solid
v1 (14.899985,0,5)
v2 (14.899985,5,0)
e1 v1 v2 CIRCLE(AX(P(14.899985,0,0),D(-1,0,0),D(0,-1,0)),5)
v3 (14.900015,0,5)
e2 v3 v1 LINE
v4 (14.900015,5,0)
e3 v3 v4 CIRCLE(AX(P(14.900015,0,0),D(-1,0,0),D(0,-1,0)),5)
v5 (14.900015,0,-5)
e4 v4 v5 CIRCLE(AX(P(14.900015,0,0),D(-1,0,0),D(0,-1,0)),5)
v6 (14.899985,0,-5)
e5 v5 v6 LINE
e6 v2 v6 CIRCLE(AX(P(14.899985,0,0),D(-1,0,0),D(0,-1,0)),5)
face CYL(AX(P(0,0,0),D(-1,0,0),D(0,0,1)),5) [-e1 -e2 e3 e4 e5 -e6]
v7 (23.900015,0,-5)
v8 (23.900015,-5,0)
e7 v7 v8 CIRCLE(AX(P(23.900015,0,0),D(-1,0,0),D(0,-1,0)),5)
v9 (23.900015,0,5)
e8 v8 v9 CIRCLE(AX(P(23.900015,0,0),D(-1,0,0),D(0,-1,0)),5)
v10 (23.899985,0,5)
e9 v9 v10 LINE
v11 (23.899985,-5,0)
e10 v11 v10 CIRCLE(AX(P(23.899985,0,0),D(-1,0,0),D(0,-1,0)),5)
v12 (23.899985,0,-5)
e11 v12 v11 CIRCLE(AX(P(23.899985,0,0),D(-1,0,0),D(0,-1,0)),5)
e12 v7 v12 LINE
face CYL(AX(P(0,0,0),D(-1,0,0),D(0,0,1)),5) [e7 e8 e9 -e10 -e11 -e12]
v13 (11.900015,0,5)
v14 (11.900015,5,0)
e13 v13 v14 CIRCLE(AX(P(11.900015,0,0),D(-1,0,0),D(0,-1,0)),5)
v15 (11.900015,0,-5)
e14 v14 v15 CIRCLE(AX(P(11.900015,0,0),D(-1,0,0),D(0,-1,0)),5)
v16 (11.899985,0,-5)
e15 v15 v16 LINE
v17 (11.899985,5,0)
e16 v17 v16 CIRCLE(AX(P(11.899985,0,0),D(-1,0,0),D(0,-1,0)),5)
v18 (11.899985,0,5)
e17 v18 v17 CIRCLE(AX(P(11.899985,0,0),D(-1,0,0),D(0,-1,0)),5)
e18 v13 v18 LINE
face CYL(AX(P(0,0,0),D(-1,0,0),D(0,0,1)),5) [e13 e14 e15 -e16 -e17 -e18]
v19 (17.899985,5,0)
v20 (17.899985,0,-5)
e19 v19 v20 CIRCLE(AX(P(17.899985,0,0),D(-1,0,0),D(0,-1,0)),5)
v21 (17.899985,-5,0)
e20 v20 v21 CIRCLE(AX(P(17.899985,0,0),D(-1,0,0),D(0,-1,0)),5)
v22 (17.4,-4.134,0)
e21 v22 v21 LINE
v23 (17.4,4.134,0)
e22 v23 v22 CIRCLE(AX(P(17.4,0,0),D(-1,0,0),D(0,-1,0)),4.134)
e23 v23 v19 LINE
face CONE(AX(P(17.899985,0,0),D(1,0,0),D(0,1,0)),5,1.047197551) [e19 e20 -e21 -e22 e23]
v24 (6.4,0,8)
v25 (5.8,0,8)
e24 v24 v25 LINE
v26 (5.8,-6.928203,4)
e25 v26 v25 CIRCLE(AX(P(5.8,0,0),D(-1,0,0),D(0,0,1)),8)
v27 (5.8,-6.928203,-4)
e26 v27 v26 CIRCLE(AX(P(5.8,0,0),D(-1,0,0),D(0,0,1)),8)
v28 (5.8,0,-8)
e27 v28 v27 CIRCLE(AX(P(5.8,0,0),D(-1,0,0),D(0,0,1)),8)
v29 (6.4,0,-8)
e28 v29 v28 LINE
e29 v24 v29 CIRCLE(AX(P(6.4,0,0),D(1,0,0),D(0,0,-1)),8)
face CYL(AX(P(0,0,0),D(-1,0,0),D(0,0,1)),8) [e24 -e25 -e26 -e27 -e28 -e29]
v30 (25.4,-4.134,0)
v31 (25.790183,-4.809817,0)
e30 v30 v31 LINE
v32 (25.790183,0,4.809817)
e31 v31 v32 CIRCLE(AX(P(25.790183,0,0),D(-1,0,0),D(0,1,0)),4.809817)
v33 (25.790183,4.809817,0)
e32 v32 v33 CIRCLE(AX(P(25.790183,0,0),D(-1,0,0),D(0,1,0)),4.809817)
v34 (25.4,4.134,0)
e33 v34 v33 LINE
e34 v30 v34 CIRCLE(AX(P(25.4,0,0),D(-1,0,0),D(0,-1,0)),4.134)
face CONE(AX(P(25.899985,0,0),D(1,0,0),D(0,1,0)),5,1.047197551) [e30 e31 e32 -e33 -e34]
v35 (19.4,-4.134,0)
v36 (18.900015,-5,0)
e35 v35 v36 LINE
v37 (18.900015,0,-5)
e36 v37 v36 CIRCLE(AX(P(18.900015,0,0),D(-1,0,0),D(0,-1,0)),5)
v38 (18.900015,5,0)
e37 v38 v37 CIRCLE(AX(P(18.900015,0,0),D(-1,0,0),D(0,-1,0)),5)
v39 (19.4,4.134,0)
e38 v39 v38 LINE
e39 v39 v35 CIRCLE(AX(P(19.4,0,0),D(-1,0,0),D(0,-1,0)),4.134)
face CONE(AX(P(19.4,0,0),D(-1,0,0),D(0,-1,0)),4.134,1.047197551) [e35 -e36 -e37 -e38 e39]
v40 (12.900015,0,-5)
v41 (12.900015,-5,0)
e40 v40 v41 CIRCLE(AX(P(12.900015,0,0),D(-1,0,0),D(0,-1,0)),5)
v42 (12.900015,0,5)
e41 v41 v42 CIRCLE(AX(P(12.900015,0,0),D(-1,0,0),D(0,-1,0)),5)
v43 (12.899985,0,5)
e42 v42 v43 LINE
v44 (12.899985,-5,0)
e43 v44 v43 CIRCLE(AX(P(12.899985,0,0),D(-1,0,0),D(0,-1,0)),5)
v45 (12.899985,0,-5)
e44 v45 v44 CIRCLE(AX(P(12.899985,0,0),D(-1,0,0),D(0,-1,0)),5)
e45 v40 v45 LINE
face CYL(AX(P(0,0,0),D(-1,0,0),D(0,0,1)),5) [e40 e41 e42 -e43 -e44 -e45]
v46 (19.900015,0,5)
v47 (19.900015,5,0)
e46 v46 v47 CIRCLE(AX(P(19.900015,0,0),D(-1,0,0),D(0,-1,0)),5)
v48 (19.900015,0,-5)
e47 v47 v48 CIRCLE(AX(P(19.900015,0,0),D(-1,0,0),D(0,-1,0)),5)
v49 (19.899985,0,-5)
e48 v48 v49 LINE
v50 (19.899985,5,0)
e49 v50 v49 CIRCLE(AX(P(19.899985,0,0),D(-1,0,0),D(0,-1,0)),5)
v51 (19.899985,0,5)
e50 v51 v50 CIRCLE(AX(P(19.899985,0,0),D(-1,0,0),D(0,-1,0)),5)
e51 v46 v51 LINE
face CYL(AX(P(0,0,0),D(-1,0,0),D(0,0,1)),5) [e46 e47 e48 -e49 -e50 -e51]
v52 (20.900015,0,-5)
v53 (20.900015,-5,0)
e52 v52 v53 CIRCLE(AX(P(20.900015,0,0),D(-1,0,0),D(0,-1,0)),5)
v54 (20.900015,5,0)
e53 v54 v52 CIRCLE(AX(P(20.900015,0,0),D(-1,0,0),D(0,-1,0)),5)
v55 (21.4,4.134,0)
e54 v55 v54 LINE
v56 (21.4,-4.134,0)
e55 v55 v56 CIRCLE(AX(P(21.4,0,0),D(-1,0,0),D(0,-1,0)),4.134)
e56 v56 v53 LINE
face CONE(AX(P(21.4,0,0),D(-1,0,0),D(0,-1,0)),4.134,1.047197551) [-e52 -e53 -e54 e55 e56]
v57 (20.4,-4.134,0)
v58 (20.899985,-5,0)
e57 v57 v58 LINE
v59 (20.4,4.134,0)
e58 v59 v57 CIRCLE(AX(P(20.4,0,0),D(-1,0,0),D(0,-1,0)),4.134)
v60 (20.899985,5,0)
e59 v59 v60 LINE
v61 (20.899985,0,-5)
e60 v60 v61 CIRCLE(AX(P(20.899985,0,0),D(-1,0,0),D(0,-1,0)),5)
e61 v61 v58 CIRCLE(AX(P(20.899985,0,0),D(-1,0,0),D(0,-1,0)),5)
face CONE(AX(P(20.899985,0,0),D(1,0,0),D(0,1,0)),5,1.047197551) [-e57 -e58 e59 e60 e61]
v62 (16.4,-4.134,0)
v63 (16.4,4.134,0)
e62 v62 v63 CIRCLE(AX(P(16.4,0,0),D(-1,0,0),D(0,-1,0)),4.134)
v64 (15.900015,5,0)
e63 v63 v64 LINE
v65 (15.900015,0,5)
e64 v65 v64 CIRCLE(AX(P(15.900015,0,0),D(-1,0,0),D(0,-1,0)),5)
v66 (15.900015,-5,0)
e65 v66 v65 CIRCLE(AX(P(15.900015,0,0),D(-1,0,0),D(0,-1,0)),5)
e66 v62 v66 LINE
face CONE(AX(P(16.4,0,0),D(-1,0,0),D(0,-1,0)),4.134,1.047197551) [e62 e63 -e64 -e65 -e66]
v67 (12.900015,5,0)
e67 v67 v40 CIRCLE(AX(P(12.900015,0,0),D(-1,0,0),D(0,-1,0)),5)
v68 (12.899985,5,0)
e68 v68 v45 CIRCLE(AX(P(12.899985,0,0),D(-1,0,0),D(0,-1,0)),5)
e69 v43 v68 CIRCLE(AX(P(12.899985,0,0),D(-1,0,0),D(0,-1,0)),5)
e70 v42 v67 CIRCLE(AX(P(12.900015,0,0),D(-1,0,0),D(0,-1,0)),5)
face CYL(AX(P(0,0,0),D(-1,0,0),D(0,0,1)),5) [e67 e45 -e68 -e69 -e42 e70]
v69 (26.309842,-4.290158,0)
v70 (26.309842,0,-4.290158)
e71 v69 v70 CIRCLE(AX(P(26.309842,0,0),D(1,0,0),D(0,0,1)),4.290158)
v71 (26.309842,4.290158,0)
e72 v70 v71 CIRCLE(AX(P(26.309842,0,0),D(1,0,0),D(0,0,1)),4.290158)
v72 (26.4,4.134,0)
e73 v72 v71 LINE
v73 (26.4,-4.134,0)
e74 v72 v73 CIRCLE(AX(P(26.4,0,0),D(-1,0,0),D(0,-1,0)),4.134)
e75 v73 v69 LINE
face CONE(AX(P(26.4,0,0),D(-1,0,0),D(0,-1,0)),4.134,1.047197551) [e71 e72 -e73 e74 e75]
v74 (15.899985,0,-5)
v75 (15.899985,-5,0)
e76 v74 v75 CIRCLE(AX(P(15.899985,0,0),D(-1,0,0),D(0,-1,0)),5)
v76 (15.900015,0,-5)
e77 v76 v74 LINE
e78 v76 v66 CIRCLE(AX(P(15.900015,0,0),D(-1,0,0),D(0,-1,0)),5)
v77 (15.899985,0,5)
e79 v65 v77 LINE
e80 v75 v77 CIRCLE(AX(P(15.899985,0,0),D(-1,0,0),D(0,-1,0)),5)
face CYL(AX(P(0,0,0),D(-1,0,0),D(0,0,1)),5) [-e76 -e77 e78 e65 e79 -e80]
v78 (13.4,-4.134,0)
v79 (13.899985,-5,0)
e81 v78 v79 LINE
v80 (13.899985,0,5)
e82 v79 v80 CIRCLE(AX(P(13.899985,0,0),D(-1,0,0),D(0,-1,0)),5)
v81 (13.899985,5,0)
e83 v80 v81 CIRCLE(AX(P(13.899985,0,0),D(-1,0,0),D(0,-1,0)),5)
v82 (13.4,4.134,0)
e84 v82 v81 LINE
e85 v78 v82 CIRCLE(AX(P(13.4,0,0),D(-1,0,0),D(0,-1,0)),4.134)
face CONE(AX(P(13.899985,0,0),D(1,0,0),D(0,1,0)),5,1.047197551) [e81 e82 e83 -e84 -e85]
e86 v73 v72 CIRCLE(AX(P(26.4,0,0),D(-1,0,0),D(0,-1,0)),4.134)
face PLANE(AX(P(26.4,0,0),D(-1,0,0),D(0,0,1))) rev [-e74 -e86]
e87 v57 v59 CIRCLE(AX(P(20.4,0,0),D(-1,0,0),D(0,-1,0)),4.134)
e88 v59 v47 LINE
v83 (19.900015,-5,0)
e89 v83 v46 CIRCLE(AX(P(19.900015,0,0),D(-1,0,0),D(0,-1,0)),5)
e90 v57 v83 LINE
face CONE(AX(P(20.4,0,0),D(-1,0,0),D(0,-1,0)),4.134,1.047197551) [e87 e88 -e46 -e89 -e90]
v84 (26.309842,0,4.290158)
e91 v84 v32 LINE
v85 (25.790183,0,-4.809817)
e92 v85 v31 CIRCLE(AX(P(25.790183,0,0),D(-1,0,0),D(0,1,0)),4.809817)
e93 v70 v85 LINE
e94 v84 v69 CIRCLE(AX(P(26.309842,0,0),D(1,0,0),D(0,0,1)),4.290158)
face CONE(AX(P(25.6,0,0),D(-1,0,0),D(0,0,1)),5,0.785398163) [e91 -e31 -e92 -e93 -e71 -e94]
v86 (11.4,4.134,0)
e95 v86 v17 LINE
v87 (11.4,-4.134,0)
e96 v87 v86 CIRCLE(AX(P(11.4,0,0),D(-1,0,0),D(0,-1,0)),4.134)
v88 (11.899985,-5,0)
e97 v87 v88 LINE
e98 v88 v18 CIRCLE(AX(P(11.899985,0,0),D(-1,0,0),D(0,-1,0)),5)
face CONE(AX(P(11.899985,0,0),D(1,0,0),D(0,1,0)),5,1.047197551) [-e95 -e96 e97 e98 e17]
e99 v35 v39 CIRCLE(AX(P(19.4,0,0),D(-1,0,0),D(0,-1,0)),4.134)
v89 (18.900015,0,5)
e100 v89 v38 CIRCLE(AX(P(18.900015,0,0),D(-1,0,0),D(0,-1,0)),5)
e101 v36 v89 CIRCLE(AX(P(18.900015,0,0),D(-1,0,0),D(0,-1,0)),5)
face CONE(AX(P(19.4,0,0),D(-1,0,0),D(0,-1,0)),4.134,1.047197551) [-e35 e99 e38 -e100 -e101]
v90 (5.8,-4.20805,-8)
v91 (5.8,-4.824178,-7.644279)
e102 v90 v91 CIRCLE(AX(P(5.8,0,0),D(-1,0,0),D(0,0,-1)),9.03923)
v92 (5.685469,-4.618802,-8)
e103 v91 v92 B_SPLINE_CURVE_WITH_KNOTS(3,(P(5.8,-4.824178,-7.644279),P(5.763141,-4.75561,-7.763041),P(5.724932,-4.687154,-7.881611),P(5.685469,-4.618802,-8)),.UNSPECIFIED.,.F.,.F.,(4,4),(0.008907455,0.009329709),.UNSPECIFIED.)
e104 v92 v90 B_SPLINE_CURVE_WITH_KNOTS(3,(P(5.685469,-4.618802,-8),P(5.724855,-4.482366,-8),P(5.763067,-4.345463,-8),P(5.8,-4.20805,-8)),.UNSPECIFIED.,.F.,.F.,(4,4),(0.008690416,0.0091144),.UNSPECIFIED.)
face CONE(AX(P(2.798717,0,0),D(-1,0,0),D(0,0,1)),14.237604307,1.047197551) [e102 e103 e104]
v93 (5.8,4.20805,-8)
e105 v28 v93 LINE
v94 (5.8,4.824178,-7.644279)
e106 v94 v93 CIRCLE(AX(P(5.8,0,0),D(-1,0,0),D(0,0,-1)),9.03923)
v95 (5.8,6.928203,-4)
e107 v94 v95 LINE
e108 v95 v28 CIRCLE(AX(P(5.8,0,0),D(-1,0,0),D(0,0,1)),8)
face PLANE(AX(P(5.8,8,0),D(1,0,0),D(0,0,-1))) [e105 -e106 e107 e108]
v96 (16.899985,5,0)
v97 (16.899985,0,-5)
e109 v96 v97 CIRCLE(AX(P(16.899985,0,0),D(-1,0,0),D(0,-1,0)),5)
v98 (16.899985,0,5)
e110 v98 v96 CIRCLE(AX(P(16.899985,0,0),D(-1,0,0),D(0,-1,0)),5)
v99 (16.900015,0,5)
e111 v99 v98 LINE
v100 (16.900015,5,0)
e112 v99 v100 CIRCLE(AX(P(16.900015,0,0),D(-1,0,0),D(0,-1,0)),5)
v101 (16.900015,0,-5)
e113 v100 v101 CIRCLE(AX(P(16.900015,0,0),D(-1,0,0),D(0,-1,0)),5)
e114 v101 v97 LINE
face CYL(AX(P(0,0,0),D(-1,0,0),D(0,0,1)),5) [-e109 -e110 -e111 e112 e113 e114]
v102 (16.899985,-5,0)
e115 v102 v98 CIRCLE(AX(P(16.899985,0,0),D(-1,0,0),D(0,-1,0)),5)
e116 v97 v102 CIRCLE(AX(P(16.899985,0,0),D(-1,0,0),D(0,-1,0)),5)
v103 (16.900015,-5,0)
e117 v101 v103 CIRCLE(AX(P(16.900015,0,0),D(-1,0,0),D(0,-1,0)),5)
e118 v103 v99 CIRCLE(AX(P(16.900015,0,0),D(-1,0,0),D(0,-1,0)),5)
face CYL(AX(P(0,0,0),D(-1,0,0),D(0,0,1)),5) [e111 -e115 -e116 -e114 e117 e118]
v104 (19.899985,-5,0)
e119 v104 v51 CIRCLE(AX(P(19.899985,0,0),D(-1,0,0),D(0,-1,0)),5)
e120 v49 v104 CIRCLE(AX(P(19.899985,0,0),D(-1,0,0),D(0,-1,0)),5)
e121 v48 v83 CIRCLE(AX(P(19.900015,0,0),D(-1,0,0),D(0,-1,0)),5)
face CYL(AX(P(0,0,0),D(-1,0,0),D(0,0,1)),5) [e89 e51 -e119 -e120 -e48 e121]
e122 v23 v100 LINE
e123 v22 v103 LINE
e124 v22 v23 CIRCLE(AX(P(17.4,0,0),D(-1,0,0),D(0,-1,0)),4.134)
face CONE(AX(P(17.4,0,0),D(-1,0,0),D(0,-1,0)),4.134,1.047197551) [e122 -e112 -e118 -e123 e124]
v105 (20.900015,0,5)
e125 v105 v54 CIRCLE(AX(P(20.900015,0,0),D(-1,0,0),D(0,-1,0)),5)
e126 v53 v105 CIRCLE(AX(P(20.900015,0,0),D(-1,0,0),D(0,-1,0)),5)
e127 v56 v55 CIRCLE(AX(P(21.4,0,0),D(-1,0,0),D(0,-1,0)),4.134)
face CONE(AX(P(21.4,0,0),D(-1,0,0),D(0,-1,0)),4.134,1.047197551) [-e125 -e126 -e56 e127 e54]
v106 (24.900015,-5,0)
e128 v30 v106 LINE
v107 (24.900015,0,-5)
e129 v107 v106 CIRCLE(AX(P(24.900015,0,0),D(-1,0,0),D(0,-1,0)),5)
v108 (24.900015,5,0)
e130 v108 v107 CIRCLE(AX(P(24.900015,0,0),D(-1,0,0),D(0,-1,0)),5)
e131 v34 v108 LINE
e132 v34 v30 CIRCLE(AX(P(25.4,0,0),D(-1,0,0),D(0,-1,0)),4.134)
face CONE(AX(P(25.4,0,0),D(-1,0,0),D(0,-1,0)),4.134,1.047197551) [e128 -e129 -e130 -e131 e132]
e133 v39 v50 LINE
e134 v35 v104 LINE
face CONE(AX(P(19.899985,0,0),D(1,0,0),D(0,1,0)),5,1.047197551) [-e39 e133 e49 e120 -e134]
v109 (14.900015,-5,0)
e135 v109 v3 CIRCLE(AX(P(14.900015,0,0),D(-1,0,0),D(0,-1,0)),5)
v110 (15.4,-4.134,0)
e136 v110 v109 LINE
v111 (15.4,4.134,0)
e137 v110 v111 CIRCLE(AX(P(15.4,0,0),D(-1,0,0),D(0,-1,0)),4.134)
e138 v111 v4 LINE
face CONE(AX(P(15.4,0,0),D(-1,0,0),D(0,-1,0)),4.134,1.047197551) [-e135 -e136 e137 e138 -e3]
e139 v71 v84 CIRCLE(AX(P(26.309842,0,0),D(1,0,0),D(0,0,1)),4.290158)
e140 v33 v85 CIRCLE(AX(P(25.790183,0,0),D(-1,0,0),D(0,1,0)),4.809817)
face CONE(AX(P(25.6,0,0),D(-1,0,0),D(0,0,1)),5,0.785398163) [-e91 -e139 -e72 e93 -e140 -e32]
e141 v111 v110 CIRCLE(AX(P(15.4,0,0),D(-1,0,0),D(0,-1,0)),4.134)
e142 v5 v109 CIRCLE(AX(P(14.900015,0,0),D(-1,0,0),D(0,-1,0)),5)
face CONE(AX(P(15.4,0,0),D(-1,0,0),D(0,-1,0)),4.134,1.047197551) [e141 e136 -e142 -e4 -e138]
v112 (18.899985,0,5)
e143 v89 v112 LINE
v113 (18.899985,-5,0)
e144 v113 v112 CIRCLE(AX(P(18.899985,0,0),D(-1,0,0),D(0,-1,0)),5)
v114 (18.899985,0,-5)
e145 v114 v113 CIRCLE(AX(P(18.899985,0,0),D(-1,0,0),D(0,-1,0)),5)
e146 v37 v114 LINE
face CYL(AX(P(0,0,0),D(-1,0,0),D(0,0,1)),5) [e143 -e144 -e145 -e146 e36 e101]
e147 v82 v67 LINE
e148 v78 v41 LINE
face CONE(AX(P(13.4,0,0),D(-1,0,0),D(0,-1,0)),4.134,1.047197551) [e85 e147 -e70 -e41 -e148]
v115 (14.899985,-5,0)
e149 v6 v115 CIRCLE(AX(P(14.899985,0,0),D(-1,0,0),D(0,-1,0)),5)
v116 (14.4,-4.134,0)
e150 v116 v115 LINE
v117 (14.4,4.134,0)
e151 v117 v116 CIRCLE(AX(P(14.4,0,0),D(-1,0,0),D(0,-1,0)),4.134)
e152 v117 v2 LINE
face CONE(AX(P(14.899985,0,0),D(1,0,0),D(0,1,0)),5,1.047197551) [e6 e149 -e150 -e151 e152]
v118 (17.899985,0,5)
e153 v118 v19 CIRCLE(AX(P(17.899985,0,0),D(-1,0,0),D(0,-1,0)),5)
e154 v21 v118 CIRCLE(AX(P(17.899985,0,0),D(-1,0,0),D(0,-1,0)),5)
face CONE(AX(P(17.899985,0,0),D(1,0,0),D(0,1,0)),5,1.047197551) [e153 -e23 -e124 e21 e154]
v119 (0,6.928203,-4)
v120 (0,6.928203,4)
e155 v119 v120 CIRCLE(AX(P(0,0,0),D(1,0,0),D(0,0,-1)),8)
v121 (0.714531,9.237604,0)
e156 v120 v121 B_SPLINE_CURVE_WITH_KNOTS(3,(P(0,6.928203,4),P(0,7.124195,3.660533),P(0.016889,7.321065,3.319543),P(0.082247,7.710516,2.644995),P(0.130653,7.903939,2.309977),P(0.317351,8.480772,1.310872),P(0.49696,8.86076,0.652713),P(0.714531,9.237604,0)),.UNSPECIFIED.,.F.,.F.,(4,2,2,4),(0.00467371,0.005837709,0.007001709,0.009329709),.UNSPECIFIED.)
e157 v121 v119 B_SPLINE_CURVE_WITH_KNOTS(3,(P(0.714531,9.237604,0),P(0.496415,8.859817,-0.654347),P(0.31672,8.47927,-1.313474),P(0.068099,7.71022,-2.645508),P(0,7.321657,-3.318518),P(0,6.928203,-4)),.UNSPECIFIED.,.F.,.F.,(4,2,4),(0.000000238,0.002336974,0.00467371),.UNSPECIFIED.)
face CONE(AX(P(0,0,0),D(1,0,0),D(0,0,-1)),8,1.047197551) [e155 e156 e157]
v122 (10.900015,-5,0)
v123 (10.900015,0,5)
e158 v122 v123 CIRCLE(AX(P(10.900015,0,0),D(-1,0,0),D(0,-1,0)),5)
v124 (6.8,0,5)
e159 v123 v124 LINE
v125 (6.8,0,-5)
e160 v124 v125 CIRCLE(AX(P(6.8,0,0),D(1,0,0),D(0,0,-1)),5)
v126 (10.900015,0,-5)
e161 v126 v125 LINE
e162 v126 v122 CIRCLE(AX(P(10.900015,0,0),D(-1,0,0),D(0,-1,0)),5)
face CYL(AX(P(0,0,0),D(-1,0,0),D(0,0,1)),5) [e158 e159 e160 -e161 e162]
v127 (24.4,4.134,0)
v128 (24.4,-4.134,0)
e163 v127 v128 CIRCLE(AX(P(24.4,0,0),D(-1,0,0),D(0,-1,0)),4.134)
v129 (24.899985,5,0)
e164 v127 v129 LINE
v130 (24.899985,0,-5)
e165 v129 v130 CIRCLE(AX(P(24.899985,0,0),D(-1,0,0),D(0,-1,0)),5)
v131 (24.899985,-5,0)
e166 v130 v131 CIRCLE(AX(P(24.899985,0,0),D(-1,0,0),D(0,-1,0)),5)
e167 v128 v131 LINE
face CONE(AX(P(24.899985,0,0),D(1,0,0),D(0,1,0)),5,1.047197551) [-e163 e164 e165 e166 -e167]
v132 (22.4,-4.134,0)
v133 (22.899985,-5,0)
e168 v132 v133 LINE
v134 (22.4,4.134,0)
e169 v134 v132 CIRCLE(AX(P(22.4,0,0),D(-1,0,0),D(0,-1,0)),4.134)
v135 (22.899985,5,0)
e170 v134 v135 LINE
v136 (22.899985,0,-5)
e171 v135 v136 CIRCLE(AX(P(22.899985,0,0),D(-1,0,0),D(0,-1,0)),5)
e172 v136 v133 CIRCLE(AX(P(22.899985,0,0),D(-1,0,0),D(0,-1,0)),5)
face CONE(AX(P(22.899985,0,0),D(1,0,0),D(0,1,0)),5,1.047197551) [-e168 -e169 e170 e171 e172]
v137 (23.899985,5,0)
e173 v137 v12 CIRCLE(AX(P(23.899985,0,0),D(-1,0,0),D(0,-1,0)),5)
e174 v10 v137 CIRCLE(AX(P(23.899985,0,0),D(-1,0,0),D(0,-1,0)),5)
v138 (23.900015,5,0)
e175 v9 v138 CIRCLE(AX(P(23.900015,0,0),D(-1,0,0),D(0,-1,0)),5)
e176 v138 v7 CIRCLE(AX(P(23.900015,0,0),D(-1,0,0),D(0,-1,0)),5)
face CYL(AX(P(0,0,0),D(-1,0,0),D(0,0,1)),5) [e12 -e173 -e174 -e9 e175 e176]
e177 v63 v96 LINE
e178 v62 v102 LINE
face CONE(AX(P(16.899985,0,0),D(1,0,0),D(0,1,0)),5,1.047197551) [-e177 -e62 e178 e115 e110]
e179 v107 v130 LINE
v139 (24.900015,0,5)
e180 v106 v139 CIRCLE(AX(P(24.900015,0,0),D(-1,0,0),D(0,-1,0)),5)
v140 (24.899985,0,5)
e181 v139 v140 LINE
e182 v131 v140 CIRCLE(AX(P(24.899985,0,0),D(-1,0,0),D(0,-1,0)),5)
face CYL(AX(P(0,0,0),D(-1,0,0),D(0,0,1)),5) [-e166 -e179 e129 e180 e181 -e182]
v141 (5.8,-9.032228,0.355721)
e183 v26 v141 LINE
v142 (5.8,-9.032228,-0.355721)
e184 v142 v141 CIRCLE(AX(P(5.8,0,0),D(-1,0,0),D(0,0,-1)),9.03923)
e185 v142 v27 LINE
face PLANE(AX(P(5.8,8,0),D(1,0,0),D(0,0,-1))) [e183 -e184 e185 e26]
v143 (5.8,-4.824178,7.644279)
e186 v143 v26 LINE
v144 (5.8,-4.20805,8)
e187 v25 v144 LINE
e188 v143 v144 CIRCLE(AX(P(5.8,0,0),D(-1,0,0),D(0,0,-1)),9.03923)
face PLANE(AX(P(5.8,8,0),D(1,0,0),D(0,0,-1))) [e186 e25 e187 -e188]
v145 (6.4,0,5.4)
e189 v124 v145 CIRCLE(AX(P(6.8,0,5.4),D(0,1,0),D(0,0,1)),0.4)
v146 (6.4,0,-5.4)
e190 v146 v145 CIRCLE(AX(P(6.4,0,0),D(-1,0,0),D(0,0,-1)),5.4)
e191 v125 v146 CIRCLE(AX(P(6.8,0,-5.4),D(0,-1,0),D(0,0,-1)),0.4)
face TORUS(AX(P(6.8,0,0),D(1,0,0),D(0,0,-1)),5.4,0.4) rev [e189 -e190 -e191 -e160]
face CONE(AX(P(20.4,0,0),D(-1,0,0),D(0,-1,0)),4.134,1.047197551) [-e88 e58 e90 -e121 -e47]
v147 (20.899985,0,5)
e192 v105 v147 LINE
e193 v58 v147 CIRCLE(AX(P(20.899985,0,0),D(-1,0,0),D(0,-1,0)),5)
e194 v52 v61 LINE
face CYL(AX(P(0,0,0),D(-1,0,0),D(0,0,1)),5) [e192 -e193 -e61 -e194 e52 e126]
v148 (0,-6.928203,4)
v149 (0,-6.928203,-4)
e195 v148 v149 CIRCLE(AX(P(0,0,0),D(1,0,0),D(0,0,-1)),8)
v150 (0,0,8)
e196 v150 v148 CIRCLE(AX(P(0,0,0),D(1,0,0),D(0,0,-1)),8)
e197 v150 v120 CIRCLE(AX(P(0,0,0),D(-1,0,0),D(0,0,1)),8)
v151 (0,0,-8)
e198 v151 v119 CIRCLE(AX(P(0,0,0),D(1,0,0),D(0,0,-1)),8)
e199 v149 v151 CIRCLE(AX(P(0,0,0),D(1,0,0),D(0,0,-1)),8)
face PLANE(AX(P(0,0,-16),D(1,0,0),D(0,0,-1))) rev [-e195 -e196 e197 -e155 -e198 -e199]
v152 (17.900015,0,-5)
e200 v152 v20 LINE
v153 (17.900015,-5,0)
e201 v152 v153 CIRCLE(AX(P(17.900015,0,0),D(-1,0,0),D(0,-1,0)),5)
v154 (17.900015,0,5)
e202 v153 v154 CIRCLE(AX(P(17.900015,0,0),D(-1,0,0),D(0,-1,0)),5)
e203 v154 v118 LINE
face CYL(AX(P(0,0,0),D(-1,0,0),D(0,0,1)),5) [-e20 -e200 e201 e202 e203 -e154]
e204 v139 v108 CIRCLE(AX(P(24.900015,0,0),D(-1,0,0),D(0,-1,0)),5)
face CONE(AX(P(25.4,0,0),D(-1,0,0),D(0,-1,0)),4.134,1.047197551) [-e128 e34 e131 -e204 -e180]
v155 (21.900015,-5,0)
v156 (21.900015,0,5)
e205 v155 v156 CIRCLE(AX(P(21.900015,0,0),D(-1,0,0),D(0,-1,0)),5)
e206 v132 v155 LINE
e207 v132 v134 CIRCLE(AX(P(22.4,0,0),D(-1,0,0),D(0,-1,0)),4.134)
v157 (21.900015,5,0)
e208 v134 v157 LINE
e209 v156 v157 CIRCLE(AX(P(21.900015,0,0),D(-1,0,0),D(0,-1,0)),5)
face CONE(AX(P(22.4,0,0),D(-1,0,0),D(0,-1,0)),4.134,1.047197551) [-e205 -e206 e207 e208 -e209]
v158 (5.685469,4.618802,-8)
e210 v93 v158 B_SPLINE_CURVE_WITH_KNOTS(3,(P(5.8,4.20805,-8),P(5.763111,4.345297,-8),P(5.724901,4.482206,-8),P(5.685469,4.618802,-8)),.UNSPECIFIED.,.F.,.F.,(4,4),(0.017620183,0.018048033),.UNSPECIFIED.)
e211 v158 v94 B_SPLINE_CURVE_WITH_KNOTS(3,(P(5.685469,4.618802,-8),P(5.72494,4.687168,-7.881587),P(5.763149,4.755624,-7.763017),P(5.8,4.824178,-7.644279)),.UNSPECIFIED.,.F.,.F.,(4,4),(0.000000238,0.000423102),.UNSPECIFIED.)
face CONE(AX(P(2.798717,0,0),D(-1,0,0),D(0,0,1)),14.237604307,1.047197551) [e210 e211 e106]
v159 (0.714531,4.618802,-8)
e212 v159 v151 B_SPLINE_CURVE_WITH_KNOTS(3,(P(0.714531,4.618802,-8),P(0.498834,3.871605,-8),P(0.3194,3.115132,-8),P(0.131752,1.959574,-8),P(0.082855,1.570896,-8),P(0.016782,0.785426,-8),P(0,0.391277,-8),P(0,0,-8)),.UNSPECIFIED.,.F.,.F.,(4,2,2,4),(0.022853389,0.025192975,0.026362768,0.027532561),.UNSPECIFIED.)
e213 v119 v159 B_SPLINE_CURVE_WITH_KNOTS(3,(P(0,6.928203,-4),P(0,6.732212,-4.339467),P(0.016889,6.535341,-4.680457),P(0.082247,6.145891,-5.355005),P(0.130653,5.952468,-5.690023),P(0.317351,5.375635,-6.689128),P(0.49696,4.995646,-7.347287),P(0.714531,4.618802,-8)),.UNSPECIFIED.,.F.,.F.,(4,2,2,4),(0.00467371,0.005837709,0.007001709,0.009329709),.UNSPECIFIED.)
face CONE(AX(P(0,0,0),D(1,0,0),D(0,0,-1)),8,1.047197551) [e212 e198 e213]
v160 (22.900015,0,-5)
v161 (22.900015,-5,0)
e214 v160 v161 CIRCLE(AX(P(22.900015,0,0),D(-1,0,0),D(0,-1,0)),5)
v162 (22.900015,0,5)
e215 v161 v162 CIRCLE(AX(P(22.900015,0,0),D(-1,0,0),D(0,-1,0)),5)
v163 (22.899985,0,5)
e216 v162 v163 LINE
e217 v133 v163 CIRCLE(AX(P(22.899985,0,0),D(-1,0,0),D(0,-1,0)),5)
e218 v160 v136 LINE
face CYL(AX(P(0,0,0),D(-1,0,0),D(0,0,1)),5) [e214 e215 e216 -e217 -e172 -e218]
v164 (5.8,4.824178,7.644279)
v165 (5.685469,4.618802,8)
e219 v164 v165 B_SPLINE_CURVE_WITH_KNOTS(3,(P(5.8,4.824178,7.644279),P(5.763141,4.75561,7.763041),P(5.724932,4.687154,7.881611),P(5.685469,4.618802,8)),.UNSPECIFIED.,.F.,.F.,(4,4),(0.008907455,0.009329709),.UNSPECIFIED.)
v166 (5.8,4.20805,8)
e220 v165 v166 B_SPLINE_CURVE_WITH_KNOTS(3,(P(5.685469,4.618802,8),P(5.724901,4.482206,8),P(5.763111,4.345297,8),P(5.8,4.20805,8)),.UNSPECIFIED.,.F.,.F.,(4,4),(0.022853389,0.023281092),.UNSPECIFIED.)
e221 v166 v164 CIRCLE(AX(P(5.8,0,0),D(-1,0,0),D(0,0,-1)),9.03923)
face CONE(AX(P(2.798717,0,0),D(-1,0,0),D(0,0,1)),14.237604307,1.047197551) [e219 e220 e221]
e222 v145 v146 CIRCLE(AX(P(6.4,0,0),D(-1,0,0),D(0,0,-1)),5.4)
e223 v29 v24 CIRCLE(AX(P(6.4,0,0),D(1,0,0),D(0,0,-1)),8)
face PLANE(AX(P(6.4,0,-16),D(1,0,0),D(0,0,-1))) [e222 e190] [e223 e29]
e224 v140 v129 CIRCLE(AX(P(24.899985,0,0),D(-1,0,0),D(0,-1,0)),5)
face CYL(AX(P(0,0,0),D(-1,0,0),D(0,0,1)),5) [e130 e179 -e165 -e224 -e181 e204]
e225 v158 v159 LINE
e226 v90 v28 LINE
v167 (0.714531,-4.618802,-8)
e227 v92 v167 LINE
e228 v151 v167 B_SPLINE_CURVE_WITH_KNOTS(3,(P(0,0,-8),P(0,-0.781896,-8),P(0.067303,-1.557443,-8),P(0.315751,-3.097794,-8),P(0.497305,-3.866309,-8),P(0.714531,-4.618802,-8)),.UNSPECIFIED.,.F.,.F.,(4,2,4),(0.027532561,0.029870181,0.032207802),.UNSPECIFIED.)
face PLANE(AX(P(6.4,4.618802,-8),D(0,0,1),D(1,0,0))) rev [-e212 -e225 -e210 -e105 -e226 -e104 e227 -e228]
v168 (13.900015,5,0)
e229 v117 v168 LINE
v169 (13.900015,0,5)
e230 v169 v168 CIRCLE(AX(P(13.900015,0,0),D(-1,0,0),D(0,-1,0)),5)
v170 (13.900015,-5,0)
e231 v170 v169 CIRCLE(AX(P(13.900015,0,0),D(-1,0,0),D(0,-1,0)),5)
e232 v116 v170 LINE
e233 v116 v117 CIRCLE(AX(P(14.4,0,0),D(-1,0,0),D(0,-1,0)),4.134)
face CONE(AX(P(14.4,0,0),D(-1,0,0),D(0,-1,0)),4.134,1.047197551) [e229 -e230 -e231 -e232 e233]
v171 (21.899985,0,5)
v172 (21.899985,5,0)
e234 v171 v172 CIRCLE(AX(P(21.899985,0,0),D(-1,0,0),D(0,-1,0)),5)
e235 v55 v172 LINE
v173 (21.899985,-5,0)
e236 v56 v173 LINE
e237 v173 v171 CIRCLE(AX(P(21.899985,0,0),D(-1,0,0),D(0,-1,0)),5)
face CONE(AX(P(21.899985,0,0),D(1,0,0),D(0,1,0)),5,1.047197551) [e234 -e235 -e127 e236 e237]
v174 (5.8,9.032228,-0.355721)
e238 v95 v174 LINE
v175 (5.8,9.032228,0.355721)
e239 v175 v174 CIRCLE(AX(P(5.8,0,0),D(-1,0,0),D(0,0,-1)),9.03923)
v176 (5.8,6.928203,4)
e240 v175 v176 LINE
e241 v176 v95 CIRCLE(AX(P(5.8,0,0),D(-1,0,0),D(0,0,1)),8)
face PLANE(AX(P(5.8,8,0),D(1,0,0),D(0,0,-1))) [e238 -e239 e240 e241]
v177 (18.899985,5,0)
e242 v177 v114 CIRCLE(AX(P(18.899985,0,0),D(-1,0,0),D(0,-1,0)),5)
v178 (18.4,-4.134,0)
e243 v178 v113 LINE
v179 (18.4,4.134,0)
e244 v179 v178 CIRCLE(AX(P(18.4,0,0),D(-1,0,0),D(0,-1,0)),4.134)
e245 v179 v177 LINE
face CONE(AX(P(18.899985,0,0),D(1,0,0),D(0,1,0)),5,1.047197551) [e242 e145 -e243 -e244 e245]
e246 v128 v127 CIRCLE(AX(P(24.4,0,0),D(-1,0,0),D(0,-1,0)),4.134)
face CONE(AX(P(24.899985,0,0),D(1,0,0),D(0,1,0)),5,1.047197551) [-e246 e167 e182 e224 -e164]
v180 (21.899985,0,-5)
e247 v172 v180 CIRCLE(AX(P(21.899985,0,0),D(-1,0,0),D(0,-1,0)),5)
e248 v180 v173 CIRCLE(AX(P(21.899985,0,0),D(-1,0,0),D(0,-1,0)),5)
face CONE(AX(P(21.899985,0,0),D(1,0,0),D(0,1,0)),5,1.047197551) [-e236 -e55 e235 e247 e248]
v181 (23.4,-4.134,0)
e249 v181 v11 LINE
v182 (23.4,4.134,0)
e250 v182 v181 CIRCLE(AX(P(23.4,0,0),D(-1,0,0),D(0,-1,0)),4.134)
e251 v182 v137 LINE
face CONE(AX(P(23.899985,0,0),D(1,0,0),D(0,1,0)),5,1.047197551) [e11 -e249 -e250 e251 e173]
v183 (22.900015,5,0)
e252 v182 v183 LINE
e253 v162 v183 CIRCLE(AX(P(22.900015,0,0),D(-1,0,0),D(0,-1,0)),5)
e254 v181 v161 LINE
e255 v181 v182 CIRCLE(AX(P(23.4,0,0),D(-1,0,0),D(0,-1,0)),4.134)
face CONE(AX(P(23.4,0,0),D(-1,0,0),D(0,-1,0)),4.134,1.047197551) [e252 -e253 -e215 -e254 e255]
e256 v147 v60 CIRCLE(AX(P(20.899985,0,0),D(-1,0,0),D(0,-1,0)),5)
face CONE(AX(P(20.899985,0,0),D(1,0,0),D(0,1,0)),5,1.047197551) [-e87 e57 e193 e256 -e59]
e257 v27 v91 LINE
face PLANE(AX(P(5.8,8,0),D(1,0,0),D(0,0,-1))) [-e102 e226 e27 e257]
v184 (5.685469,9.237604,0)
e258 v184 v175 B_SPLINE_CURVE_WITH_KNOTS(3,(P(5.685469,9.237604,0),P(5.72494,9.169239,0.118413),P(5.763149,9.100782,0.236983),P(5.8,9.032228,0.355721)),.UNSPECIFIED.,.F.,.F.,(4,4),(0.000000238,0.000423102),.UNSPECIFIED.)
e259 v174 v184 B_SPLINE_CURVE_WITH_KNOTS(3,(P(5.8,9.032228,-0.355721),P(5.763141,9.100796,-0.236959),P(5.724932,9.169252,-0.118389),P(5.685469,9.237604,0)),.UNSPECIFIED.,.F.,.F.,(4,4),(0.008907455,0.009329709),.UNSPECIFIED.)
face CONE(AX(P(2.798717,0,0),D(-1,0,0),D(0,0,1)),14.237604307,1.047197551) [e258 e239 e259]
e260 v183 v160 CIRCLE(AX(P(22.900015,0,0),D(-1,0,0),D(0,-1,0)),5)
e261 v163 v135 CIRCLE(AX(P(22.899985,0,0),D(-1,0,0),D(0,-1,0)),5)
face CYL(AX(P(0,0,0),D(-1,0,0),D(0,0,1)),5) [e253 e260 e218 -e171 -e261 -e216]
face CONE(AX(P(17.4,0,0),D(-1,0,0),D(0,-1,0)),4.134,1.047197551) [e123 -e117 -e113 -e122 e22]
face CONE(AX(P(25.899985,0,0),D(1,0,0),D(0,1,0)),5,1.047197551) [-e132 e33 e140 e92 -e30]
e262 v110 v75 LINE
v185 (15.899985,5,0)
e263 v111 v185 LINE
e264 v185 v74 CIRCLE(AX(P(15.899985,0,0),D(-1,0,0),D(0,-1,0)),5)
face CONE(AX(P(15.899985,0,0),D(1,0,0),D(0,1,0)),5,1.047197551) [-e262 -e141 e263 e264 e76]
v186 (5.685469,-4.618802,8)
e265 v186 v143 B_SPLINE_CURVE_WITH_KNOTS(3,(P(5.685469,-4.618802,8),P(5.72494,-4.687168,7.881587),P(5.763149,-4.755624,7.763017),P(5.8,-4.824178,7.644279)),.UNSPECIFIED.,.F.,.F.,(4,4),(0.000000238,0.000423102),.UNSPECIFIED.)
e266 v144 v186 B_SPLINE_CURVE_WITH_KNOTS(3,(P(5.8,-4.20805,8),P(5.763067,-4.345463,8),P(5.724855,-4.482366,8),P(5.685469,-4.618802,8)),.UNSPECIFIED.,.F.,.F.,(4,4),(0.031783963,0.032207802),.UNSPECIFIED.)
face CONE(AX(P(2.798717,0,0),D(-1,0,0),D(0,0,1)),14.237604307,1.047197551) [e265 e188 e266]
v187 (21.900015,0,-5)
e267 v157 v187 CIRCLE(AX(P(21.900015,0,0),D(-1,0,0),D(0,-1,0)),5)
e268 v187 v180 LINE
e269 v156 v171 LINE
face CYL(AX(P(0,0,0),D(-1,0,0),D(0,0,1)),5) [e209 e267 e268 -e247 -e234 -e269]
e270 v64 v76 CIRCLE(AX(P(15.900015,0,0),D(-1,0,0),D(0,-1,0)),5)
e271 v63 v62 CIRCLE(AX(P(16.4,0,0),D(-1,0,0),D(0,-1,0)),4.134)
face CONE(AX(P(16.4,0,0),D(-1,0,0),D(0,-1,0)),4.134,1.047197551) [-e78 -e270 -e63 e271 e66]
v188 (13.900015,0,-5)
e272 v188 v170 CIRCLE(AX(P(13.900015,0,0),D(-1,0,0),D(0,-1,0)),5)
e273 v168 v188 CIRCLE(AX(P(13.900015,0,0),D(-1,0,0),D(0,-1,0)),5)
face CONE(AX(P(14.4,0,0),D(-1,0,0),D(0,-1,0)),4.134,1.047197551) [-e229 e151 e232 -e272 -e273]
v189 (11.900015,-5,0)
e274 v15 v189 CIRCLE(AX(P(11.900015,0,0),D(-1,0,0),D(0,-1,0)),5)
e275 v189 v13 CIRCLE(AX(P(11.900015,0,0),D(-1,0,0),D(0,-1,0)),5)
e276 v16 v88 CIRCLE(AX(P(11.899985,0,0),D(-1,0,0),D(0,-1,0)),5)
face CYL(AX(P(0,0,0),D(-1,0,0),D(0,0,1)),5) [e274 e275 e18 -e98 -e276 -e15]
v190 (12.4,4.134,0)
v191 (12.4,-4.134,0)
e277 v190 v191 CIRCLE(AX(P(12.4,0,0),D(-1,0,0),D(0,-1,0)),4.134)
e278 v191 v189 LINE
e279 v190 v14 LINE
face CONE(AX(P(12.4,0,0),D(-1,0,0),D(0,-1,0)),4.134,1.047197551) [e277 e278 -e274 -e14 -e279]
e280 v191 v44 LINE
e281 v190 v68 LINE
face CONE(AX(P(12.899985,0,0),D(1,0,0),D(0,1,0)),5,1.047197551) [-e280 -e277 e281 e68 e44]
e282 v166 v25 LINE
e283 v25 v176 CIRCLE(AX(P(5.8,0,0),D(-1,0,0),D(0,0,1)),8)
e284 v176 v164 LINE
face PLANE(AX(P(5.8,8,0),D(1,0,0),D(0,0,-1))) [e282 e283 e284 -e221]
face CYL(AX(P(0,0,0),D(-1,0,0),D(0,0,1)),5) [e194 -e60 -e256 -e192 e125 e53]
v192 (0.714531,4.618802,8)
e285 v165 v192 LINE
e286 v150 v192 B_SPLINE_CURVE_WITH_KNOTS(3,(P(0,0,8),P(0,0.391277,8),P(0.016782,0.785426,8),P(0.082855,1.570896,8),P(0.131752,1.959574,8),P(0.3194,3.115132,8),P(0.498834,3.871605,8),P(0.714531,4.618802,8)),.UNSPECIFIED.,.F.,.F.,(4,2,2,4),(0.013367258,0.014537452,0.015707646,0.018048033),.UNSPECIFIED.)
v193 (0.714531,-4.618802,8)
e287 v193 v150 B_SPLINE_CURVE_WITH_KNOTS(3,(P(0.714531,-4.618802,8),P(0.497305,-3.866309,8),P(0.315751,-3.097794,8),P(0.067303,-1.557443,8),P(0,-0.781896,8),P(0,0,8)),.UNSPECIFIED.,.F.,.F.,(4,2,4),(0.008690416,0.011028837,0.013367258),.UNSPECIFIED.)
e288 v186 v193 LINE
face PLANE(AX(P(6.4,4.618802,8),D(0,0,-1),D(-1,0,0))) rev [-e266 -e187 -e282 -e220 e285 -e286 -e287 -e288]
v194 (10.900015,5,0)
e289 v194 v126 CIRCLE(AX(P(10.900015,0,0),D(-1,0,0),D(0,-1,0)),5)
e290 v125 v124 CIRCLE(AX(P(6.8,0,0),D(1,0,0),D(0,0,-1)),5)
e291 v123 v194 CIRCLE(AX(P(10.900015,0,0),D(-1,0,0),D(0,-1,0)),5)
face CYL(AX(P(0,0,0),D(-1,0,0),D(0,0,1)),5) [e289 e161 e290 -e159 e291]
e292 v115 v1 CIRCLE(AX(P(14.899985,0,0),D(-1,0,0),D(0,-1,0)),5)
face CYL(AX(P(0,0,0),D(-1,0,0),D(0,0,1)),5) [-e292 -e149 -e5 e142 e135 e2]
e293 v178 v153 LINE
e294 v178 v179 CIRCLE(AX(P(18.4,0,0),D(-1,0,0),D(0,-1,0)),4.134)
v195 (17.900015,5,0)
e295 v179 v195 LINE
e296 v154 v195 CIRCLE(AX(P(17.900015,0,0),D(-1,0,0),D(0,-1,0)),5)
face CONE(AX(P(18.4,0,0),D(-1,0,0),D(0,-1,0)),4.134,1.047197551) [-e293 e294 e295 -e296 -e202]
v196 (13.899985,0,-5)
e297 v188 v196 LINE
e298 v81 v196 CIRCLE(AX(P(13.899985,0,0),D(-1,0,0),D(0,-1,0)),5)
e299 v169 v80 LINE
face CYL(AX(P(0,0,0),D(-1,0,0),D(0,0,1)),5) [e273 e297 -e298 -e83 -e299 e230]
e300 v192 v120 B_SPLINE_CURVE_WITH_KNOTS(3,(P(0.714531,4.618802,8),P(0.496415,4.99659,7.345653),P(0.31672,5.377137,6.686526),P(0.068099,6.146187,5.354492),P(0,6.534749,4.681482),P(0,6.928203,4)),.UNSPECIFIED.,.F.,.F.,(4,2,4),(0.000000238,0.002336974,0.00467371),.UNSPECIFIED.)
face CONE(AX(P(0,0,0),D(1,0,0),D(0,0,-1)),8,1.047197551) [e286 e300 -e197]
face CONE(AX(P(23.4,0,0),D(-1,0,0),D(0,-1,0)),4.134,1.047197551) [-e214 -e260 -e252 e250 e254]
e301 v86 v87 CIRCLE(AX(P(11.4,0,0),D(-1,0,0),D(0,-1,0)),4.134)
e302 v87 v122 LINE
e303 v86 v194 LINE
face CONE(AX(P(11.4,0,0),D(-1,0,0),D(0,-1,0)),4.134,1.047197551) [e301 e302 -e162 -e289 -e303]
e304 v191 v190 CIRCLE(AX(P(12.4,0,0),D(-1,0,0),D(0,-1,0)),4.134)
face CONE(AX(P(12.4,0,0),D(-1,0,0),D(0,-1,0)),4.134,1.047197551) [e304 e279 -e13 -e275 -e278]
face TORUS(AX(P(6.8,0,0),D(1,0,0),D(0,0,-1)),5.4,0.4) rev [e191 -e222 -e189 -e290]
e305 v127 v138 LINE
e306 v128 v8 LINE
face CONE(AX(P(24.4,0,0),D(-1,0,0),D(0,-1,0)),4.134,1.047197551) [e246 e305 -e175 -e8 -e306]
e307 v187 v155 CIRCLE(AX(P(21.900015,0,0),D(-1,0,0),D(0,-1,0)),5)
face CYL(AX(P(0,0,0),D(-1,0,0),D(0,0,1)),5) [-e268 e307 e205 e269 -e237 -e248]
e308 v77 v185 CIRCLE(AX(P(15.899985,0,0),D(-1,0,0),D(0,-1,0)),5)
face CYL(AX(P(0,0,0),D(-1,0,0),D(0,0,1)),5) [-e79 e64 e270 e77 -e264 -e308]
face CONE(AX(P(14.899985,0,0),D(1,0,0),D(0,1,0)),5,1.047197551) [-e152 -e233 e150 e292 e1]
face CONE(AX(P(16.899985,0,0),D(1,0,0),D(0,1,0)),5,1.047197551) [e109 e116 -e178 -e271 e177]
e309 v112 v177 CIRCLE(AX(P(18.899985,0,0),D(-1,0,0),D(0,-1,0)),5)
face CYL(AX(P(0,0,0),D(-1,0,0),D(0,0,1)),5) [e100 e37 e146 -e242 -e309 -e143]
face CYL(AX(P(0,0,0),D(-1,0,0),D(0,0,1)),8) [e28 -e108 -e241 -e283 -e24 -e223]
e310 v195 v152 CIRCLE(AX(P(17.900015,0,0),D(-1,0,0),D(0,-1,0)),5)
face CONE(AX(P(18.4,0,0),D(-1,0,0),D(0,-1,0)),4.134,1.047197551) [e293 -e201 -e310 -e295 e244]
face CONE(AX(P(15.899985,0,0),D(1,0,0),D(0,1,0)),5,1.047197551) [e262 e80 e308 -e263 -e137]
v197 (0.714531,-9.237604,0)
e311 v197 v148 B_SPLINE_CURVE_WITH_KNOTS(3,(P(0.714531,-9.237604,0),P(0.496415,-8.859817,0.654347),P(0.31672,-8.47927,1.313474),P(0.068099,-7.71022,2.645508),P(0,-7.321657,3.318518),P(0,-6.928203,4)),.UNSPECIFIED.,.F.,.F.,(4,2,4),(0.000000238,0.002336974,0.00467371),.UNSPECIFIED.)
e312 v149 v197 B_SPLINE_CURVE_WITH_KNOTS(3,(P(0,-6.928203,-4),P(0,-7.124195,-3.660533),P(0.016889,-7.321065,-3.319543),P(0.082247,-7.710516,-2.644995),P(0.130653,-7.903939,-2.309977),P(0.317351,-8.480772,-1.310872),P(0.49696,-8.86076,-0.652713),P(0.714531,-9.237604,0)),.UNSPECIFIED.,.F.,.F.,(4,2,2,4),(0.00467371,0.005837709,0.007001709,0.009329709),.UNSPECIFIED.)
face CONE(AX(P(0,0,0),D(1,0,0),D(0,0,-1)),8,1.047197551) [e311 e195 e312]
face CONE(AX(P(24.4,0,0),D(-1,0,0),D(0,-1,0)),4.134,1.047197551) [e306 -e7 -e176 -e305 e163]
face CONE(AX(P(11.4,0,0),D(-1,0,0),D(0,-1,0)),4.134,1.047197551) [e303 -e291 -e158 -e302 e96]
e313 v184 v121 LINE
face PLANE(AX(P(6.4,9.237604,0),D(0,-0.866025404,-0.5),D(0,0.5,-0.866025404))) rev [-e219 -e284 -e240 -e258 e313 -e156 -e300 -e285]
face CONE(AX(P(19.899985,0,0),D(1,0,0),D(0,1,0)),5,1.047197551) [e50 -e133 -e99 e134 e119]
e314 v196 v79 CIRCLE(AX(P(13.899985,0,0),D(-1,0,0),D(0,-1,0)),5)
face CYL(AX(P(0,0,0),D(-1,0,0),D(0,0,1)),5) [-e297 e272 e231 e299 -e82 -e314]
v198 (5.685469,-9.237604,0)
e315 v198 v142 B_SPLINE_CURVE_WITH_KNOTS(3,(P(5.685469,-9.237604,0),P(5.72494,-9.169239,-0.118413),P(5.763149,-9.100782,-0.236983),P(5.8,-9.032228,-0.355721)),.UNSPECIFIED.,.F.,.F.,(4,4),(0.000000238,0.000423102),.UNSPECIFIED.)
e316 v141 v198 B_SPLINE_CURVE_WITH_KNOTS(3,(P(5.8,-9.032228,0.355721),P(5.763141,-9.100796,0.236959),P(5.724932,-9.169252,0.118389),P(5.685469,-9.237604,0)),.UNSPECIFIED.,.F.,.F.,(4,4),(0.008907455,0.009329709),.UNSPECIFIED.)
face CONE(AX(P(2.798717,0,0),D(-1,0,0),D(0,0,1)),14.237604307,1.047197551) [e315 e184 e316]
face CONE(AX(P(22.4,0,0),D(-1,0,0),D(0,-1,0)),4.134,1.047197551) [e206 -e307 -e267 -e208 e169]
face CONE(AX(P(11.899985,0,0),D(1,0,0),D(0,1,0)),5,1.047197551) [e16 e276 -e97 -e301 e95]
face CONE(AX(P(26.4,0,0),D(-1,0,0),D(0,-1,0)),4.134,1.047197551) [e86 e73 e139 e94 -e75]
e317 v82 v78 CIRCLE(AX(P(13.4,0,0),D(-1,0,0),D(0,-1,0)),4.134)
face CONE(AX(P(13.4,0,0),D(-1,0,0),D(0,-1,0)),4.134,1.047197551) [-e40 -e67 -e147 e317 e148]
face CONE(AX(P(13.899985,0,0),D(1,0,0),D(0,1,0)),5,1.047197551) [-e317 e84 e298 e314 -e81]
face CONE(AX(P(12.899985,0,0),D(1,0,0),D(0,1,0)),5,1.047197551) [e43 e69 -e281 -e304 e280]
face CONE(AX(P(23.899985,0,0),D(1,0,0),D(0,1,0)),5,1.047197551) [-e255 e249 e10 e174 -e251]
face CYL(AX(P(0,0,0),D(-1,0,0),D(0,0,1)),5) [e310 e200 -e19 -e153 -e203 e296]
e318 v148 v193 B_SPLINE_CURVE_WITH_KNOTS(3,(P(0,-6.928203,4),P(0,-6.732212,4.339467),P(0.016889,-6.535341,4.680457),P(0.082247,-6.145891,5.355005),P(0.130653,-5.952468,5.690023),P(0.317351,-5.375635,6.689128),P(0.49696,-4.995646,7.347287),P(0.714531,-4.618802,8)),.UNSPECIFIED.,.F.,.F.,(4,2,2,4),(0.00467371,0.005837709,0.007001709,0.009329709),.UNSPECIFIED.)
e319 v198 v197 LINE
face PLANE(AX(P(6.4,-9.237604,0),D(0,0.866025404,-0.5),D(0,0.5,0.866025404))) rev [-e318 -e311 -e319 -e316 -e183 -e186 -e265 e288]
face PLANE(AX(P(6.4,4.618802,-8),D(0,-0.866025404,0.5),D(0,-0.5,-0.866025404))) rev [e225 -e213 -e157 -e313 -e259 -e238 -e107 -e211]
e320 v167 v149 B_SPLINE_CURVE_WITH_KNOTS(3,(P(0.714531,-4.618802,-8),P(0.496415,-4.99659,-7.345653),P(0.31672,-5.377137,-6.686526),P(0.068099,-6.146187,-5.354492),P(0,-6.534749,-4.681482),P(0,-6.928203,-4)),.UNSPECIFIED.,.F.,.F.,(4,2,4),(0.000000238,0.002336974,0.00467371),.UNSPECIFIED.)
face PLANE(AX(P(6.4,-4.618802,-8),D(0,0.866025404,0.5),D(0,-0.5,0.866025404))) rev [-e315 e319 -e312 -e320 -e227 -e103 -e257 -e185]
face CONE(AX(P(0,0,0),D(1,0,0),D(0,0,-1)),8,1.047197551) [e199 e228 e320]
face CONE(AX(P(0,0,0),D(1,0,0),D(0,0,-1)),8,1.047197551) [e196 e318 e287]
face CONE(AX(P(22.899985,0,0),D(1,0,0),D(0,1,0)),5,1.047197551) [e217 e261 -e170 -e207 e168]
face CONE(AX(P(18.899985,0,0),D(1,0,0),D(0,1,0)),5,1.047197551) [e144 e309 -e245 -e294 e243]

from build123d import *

# Parameters (mm, degrees)
EXTRUDE_393_DEPTH      = 6.4
SKETCH_4_W             = 0.6
SKETCH_4_H             = 11.237604307
CHAMFER_2072_SIZE      = 0.8
FILLET_2117_R          = 0.4
PATTERN_LINEAR_1_COUNT = 16
PATTERN_LINEAR_1_PITCH = 1


with BuildPart() as part:
    # 草图1 → Extrude 393 (new body)
    with BuildSketch(Plane(origin=(0, 0, 0), x_dir=(0, 0, -1), z_dir=(1, 0, 0))):
        Polygon((8, 4.618802154), (8, -4.618802154), (0, -9.237604307), (-8, -4.618802154), (-8, 4.618802154), (0, 9.237604307), align=None)
    extrude(amount=EXTRUDE_393_DEPTH)

    # 草图2 → 凸台-旋转1 (revolve)
    with BuildSketch(Plane.XY, mode=Mode.PRIVATE) as revolve_1_sk:
        Polygon((0, 0), (26.4, 0), (26.4, 4.134), (26.4, 5), (0, 5), align=None)
    revolve(revolve_1_sk.sketch.rotate(Axis((0, 0, 0), (1, 0, 0)), 90), axis=Axis((0, 0, 0), (1, 0, 0)))

    # 草图3 → 切除-旋转1 (revolve, cut)
    with BuildSketch(Plane.XY):
        Polygon((0, 8), (3.601282526, 14.237604307), (3.601282526, 19.237604307), (-10, 19.237604307), (-10, 8), align=None)
    revolve(axis=Axis((0, 0, 0), (1, 0, 0)), mode=Mode.SUBTRACT)

    # 草图5 → 切除-旋转2 (revolve, cut)
    with BuildSketch(Plane.XY):
        Polygon((6.4, 8), (2.798717474, 14.237604307), (2.798717474, 19.237604307), (12.798717474, 19.237604307), (12.798717474, 8), align=None)
    revolve(axis=Axis((0, 0, 0), (1, 0, 0)), mode=Mode.SUBTRACT)

    # 草图4 → 切除-旋转3 (revolve, cut)
    with BuildSketch(Plane.XY, mode=Mode.PRIVATE) as cut_revolve_3_sk:
        with Locations((6.1, 13.618802154)):
            Rectangle(SKETCH_4_W, SKETCH_4_H)
    revolve(cut_revolve_3_sk.sketch.rotate(Axis((0, 0, 0), (1, 0, 0)), 270), axis=Axis((0, 0, 0), (1, 0, 0)), mode=Mode.SUBTRACT)

    # Chamfer 2072
    chamfer_2072_edges = [part.edges().sort_by_distance(p)[0] for p in [
        (26.4, 0, -5),
    ]]
    chamfer(chamfer_2072_edges, length=CHAMFER_2072_SIZE)

    # Fillet 2117
    fillet_2117_edges = [part.edges().sort_by_distance(p)[0] for p in [
        (6.4, 0, -5),
    ]]
    fillet(fillet_2117_edges, radius=FILLET_2117_R)

    # 草图6 → 切除-旋转4 (revolve, cut)
    with BuildSketch(Plane.XY):
        Polygon((11.4, -4.134), (10.900014667, -5), (10.900014667, -6.25), (11.899985333, -6.25), (11.899985333, -5), align=None)
    cut_revolve_4 = revolve(axis=Axis((-3.175, 0, 0), (1, 0, 0)), mode=Mode.SUBTRACT)

    # 阵列(线性)1: 切除-旋转4 ×16
    with Locations(*[(i * PATTERN_LINEAR_1_PITCH, 0, 0) for i in range(1, PATTERN_LINEAR_1_COUNT)]):
        add(cut_revolve_4, mode=Mode.SUBTRACT)


solid = part.part
